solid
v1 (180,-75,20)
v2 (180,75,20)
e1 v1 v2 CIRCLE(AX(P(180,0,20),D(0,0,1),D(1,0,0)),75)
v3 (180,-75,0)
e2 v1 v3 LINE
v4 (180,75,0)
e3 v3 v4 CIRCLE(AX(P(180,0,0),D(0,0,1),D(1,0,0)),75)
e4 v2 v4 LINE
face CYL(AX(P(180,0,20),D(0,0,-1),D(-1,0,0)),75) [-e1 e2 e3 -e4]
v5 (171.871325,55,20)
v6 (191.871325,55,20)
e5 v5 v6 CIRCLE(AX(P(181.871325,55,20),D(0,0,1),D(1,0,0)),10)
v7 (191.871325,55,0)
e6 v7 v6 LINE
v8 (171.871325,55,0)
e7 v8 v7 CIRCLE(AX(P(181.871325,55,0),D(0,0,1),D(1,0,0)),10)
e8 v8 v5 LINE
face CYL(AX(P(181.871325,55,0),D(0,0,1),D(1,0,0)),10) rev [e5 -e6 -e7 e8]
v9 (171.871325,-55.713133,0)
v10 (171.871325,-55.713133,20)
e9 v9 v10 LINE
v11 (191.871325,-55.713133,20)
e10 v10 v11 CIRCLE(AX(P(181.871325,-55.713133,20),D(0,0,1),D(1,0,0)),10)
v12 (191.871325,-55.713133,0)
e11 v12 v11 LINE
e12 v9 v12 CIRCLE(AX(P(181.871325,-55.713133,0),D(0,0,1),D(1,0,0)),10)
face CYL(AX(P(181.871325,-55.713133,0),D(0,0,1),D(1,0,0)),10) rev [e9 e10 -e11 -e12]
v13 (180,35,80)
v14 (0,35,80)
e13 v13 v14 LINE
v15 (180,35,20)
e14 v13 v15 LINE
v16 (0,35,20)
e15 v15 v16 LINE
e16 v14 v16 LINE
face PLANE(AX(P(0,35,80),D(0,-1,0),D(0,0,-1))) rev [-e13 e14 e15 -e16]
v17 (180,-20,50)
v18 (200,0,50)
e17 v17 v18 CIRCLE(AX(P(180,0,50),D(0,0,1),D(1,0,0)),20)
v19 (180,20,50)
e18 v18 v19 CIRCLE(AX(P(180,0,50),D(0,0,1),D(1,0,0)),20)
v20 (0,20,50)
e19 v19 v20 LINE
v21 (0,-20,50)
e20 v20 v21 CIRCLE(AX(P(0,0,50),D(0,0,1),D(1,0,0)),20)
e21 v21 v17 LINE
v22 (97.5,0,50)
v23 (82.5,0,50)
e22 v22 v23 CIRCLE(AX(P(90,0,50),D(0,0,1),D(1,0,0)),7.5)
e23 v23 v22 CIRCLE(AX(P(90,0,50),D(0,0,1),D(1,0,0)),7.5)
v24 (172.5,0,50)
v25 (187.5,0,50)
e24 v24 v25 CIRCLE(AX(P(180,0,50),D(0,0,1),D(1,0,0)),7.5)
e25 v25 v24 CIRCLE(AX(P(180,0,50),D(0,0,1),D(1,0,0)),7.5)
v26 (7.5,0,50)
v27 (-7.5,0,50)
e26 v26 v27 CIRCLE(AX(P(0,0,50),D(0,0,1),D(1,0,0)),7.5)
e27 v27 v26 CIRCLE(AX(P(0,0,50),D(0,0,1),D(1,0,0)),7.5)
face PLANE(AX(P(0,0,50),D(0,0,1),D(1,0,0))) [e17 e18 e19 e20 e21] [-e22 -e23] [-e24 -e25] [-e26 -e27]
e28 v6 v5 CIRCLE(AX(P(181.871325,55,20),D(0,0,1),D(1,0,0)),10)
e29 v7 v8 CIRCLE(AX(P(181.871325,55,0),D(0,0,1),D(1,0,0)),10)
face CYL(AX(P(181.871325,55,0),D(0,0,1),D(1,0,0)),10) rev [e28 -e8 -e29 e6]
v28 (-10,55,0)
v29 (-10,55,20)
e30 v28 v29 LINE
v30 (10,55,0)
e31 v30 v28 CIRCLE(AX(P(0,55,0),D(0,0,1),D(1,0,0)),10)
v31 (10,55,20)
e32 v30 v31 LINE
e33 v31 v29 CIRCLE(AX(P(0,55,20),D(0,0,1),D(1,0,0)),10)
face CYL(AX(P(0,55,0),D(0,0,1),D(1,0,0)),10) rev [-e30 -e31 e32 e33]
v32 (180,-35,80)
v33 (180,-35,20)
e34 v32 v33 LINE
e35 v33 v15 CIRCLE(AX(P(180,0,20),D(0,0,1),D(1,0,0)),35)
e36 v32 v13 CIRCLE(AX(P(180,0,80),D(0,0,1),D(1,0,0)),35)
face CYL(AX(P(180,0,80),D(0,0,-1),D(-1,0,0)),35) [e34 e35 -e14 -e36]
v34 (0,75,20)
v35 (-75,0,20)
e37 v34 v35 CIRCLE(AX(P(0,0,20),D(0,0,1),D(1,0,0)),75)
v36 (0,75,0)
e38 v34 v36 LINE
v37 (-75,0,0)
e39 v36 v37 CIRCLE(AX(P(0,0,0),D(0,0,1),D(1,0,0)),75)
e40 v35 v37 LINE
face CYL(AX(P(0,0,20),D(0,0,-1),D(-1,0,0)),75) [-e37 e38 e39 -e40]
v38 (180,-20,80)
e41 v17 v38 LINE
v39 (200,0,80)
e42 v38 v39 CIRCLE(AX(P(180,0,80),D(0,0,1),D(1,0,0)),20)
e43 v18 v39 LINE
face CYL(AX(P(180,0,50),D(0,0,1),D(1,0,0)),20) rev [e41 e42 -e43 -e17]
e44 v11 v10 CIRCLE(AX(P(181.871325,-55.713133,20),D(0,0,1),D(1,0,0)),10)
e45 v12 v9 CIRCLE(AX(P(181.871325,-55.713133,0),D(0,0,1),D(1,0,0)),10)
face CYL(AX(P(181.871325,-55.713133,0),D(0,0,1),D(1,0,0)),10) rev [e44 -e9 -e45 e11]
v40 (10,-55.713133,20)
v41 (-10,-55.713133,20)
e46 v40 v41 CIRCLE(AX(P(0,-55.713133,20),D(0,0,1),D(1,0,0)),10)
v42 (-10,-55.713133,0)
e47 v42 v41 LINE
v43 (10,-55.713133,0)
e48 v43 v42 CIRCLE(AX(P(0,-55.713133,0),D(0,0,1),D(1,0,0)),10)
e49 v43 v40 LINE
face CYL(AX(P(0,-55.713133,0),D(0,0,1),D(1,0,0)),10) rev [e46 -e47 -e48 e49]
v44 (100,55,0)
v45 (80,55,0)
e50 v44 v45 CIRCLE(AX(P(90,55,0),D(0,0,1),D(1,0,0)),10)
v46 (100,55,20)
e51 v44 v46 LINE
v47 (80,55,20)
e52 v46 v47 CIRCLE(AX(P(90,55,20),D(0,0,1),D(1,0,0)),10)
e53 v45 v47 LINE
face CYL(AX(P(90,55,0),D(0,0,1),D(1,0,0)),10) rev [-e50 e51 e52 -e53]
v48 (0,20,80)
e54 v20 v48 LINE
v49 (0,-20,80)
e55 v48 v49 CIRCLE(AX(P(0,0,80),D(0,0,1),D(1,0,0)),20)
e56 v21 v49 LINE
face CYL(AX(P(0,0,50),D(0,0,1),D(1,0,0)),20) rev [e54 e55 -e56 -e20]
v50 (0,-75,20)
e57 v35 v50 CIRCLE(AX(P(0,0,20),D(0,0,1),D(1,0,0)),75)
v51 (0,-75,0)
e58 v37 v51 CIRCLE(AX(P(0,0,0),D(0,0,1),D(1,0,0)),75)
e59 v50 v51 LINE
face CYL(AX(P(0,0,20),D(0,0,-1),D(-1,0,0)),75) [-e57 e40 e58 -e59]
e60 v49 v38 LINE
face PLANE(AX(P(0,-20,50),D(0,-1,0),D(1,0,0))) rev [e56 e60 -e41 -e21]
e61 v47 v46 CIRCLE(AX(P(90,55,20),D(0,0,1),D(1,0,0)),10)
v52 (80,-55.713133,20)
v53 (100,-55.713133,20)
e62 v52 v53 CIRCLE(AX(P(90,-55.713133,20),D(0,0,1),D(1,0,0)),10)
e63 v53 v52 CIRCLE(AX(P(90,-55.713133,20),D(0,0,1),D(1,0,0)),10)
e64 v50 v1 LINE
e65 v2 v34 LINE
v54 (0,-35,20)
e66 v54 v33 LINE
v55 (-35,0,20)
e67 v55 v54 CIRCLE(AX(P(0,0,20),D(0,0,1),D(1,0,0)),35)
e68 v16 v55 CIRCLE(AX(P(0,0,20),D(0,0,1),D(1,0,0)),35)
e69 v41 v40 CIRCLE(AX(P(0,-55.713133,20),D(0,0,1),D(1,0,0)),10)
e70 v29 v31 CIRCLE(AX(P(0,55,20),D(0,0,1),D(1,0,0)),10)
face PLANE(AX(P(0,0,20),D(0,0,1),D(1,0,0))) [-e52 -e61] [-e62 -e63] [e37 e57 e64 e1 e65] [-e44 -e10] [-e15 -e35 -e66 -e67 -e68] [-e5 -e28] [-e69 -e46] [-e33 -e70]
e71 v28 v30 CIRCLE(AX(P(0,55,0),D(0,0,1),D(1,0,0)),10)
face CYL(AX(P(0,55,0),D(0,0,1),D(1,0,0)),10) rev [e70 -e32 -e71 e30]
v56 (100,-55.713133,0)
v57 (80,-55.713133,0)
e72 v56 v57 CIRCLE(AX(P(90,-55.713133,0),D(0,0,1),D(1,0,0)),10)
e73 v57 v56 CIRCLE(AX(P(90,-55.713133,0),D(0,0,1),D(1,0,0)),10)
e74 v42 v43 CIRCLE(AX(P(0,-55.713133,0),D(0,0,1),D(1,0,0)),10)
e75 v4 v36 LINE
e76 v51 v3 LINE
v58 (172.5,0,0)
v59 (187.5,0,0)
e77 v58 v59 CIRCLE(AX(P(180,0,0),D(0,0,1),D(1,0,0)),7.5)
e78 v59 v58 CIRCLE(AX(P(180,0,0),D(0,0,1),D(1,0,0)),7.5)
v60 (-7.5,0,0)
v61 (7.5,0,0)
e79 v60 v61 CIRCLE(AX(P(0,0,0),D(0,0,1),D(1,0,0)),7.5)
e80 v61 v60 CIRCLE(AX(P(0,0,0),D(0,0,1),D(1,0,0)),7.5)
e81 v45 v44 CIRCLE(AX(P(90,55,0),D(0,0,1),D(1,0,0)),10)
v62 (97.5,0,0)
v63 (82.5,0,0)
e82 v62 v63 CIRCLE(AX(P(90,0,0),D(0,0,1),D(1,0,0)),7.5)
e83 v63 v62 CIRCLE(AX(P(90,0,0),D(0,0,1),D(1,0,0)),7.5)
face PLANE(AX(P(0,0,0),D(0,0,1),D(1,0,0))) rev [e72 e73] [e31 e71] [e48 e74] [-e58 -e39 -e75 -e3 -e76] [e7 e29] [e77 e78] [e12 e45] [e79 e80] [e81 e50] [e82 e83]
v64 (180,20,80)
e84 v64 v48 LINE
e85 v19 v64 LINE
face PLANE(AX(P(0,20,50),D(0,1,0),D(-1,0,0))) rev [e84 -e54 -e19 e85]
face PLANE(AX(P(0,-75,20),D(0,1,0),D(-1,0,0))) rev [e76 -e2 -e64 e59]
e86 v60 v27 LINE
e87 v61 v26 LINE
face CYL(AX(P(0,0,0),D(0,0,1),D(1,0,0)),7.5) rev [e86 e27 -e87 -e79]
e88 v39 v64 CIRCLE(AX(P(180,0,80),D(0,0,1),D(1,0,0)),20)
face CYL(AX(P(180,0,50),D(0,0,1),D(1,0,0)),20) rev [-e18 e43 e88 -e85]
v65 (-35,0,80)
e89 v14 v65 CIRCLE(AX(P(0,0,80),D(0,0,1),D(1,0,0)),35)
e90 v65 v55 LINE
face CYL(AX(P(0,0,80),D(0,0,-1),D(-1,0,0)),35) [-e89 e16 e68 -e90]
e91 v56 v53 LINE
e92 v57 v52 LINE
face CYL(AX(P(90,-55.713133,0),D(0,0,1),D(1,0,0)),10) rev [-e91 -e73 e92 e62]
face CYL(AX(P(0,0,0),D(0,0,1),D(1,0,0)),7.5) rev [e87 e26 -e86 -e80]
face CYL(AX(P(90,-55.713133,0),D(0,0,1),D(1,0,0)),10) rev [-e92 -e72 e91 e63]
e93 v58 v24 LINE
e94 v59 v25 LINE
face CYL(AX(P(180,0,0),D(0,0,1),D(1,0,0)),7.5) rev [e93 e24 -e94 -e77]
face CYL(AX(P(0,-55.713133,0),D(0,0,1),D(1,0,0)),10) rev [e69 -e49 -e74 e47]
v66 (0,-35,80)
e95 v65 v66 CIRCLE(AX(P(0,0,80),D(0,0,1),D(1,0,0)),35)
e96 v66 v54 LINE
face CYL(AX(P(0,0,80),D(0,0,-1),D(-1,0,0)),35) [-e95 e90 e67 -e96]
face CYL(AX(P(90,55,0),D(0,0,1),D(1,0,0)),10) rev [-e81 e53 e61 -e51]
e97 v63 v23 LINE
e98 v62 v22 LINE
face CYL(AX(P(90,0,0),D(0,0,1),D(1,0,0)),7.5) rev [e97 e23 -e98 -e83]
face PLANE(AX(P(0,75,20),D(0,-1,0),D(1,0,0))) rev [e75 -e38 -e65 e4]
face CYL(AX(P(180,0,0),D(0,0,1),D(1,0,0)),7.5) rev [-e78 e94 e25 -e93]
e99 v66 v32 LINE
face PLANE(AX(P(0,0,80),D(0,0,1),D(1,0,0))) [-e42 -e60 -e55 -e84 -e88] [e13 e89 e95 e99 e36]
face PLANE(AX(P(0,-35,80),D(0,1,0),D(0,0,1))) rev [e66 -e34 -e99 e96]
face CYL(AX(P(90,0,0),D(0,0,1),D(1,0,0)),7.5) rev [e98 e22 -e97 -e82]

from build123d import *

# Parameters (mm, degrees)
FLANGE_PLATE_DEPTH       = 20
OBROUND_NECK_BOSS_DEPTH  = 60
NECK_POCKET_DEPTH        = 30
THROUGH_OPENING_SKETCH_R = 7.5
THROUGH_OPENING_DEPTH    = 50
MOUNTING_HOLES_SKETCH_R  = 10
MOUNTING_HOLES_DEPTH     = 20


with BuildPart() as part:
    # Flange Plate Sketch → Flange Plate (new body)
    with BuildSketch(Plane.XY):
        with BuildLine():
            Line((0, 75), (180, 75))
            ThreePointArc((180, 75), (255, 0), (180, -75))
            Line((180, -75), (0, -75))
            ThreePointArc((0, -75), (-75, 0), (0, 75))
        make_face()
    extrude(amount=FLANGE_PLATE_DEPTH)

    # Neck Boss Sketch → Obround Neck Boss (add)
    with BuildSketch(Plane.XY.offset(20)):
        with BuildLine():
            Line((0, 35), (180, 35))
            ThreePointArc((180, 35), (215, 0), (180, -35))
            Line((180, -35), (0, -35))
            ThreePointArc((0, -35), (-35, 0), (0, 35))
        make_face()
    extrude(amount=OBROUND_NECK_BOSS_DEPTH)

    # Neck Pocket Sketch → Neck Pocket (cut)
    with BuildSketch(Plane.XY.offset(80)):
        with BuildLine():
            Line((0, 20), (180, 20))
            ThreePointArc((180, 20), (200, 0), (180, -20))
            Line((180, -20), (0, -20))
            ThreePointArc((0, -20), (-20, 0), (0, 20))
        make_face()
    extrude(amount=-NECK_POCKET_DEPTH, mode=Mode.SUBTRACT)

    # Through Opening Sketch → Through Opening (cut)
    with BuildSketch(Plane.XY.offset(50)):
        Circle(THROUGH_OPENING_SKETCH_R)
        with Locations((180, 0)):
            Circle(THROUGH_OPENING_SKETCH_R)
        with Locations((90, 0)):
            Circle(THROUGH_OPENING_SKETCH_R)
    extrude(amount=-THROUGH_OPENING_DEPTH, mode=Mode.SUBTRACT)

    # Mounting Holes Sketch → Mounting Holes (cut)
    with BuildSketch(Plane.XY.offset(20)):
        with Locations((0, 55)):
            Circle(MOUNTING_HOLES_SKETCH_R)
        with Locations((181.871324801, 55)):
            Circle(MOUNTING_HOLES_SKETCH_R)
        with Locations((181.871324801, -55.713132711)):
            Circle(MOUNTING_HOLES_SKETCH_R)
        with Locations((0, -55.713132711)):
            Circle(MOUNTING_HOLES_SKETCH_R)
        with Locations((90, 55)):
            Circle(MOUNTING_HOLES_SKETCH_R)
        with Locations((90, -55.713132711)):
            Circle(MOUNTING_HOLES_SKETCH_R)
    extrude(amount=-MOUNTING_HOLES_DEPTH, mode=Mode.SUBTRACT)


solid = part.part
